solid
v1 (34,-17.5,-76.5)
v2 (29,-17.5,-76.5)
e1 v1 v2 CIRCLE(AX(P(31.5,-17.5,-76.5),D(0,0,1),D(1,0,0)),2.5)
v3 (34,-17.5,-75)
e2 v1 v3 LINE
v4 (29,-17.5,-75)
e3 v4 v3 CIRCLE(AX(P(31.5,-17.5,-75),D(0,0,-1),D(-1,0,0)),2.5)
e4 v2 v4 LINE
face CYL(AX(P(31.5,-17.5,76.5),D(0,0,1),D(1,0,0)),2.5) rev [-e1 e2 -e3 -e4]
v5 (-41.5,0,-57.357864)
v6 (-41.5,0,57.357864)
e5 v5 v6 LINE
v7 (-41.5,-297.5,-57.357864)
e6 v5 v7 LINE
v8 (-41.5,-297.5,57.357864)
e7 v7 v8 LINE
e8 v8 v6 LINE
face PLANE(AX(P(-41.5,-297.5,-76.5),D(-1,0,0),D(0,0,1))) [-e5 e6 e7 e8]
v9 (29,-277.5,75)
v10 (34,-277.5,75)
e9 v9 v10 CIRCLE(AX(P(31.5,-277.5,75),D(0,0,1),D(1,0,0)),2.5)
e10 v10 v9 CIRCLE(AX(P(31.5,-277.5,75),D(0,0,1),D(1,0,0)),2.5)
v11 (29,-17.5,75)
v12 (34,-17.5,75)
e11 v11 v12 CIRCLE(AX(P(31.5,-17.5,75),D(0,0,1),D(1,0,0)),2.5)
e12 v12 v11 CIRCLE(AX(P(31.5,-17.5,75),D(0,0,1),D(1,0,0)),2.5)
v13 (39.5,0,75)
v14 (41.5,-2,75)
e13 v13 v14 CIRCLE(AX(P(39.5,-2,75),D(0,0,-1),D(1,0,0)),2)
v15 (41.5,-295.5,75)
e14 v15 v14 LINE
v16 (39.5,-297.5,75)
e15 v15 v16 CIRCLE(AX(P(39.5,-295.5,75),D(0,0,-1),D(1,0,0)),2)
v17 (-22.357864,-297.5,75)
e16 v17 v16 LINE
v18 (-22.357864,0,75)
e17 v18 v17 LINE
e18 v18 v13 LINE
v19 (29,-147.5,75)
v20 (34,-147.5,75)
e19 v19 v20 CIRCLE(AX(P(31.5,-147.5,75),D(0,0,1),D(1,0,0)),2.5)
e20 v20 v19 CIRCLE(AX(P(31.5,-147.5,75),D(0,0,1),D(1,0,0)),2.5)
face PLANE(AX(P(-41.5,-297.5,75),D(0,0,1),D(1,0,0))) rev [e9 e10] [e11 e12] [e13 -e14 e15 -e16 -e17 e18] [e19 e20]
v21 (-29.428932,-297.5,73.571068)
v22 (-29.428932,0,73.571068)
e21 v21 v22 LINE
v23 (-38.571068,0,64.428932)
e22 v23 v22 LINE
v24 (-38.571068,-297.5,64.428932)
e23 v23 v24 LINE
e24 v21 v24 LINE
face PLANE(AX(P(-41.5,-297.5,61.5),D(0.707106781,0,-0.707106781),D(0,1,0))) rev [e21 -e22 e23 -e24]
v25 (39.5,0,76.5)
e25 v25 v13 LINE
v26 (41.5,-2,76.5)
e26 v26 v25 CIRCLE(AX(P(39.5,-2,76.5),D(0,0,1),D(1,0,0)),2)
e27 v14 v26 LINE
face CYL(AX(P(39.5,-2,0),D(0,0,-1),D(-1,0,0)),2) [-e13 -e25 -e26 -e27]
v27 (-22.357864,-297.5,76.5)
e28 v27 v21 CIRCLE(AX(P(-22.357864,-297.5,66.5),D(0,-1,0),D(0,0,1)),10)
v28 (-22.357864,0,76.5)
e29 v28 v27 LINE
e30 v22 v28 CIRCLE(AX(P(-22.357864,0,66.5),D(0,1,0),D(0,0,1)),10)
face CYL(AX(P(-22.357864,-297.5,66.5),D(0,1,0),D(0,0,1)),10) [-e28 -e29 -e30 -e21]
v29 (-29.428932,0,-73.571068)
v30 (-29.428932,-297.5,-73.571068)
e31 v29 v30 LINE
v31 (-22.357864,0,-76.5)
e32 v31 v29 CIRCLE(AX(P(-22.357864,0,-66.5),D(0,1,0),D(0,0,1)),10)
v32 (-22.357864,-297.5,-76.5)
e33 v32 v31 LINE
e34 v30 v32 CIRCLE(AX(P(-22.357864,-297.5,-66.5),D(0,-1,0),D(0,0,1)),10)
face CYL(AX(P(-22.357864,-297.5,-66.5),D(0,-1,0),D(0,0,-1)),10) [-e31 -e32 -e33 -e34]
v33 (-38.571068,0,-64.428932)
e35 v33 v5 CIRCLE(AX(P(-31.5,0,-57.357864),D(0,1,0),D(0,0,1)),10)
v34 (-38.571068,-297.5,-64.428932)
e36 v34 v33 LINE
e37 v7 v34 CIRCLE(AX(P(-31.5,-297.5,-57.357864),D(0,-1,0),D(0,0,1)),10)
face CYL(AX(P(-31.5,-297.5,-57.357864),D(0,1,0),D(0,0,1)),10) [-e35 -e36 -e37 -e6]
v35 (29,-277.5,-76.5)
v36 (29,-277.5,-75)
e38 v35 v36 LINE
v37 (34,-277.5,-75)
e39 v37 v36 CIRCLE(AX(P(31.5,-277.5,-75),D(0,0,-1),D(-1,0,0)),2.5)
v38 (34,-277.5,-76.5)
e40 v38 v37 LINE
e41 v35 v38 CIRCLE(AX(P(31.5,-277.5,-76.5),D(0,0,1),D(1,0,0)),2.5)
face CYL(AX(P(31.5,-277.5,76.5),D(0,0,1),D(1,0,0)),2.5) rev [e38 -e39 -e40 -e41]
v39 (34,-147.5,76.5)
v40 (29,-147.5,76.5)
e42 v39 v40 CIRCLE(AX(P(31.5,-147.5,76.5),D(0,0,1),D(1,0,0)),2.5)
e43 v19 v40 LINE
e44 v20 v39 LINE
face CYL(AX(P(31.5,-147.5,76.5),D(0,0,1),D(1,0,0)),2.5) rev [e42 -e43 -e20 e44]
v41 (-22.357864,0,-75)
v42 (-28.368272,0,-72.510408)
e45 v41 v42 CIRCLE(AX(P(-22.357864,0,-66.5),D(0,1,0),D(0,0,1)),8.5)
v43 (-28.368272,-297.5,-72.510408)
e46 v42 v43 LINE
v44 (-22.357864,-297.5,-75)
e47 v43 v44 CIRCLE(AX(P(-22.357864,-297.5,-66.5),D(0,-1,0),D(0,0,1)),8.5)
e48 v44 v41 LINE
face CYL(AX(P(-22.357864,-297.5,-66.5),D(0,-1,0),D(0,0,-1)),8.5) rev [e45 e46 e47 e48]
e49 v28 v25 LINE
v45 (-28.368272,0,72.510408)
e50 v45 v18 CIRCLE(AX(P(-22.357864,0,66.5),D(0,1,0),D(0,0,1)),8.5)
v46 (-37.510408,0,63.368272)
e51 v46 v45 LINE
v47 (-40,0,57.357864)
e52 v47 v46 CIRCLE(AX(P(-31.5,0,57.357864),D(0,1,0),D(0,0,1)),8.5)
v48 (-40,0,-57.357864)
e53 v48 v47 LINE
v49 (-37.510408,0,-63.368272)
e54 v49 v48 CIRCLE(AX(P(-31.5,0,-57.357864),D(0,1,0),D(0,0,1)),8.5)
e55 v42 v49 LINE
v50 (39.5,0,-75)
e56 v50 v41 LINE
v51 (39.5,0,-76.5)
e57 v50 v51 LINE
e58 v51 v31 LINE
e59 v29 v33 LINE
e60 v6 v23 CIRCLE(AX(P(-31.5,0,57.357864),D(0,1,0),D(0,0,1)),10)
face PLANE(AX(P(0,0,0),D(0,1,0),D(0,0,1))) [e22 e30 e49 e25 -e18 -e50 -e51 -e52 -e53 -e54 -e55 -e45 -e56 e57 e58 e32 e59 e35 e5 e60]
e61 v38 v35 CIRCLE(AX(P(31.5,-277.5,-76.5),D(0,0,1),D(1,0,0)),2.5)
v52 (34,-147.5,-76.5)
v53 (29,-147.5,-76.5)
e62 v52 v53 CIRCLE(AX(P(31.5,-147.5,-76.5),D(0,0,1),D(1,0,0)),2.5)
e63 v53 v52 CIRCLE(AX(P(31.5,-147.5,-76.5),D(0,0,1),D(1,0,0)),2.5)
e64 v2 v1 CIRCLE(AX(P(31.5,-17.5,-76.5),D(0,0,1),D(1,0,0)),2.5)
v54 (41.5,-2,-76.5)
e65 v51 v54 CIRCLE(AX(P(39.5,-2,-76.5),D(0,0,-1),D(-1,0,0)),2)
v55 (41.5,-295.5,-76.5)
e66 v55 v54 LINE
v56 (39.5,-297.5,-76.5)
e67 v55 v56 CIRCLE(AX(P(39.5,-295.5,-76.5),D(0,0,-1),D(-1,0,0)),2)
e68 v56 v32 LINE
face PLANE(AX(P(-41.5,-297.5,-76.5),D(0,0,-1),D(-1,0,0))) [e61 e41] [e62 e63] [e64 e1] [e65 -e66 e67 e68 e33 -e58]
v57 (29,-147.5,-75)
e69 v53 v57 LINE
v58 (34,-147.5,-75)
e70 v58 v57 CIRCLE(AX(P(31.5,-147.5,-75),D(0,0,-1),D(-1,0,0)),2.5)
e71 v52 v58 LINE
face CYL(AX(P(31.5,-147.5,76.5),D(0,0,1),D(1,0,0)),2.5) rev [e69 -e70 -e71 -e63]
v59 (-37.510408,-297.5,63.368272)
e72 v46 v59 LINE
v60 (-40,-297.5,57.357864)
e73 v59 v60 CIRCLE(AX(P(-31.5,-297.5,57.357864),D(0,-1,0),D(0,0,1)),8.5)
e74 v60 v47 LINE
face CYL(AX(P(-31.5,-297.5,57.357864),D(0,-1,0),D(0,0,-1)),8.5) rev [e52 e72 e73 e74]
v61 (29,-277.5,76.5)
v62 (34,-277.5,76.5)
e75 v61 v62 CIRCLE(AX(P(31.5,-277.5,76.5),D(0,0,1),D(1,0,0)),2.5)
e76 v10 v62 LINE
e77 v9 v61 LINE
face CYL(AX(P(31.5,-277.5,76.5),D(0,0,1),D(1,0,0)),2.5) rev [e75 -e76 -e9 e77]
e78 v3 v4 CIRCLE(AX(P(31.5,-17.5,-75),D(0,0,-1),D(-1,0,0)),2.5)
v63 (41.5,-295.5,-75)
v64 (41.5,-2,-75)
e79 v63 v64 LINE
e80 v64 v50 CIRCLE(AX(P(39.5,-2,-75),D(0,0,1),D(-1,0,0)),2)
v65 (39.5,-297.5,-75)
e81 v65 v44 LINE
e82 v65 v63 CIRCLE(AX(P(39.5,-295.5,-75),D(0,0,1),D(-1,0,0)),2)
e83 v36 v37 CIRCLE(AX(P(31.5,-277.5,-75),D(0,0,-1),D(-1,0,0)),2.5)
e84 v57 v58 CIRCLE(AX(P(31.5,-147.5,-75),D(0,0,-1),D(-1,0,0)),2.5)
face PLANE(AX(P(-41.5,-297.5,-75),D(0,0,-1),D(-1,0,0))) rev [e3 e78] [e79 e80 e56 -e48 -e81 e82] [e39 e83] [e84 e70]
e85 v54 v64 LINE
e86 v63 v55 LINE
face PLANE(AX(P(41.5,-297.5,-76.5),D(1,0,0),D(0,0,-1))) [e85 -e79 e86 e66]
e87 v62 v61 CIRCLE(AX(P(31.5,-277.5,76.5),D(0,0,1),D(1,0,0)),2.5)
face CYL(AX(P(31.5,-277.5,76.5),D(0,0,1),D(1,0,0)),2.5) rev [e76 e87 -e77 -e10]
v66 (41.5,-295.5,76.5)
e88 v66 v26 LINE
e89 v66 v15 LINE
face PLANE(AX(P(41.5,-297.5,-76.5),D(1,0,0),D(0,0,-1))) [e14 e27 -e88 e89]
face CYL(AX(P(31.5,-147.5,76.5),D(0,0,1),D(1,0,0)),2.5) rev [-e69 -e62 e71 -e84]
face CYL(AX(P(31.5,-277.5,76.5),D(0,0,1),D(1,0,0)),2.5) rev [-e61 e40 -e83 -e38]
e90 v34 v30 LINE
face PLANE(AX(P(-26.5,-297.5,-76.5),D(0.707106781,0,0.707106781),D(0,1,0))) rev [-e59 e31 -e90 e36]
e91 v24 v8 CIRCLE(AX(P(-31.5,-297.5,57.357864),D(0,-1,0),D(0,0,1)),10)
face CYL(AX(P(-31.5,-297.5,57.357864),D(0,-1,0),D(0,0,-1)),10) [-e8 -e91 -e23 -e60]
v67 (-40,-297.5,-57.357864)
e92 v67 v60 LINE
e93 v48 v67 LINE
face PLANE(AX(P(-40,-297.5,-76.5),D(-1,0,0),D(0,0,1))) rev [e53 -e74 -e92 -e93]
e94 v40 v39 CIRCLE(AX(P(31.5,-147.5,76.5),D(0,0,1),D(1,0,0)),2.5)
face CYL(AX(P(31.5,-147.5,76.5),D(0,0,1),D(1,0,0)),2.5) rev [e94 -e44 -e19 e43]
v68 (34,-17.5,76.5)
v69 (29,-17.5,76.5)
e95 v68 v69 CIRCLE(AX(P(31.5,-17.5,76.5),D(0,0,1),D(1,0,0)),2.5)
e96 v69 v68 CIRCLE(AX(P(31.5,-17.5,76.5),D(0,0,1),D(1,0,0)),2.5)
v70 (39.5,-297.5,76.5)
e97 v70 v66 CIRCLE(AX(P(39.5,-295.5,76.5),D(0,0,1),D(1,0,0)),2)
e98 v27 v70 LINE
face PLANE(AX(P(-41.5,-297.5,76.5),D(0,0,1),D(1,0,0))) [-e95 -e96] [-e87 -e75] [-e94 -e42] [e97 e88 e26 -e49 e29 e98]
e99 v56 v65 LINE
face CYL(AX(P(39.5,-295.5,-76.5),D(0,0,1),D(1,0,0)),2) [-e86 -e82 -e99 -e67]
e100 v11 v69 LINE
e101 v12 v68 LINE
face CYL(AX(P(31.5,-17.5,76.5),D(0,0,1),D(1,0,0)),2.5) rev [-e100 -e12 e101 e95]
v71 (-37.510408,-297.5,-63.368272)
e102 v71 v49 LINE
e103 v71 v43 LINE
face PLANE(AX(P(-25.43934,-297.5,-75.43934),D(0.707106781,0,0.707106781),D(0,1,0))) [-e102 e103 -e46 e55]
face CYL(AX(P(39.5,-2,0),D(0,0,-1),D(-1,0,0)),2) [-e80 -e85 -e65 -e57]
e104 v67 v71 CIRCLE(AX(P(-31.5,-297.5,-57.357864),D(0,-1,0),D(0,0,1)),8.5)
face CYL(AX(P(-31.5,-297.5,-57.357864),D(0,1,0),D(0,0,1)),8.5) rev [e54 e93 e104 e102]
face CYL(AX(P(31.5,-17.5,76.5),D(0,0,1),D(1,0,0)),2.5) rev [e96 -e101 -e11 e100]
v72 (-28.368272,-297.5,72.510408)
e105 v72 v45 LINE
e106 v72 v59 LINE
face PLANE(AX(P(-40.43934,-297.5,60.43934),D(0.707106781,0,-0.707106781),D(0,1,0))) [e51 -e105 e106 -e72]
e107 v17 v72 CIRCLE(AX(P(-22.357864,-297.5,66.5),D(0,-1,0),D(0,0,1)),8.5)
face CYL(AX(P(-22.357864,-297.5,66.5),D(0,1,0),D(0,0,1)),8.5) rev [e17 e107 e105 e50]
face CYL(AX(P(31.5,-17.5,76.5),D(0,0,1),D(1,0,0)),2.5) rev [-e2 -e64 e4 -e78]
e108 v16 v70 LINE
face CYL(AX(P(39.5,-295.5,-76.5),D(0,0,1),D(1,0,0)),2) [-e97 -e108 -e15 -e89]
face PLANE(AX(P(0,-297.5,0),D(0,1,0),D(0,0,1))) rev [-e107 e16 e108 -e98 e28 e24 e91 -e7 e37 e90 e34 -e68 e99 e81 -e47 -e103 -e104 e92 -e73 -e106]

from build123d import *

# Parameters (mm, degrees)
SKETCH_2_W            = 83
SKETCH_2_H            = 153
EXTRUDE_2_DEPTH       = 297.5
CHAMFER_1_SIZE        = 15
FILLET_1_R            = 10
SHELL_2_T             = -1.5
HOLE_WIZARD_5_0_5_1_D = 5
FILLET_2_R            = 2


with BuildPart() as part:
    # 草图2 → 凸台-拉伸2 (new body)
    with BuildSketch(Plane(origin=(0, 0, 0), x_dir=(1, 0, 0), z_dir=(0, 1, 0))):
        Rectangle(SKETCH_2_W, SKETCH_2_H)
    extrude(amount=-EXTRUDE_2_DEPTH)

    # 倒角1
    chamfer_1_edges = [part.edges().sort_by_distance(p)[0] for p in [
        (-41.5, -148.75, 76.5),
        (-41.5, -148.75, -76.5),
    ]]
    chamfer(chamfer_1_edges, length=CHAMFER_1_SIZE)

    # 圆角1
    fillet_1_edges = [part.edges().sort_by_distance(p)[0] for p in [
        (-26.5, -148.75, -76.5),
        (-41.5, -148.75, 61.5),
        (-41.5, -148.75, -61.5),
        (-26.5, -148.75, 76.5),
    ]]
    fillet(fillet_1_edges, radius=FILLET_1_R)

    # 抽壳2
    shell_2_openings = [part.faces().sort_by_distance(p)[0] for p in [
        (0.682002961, -297.5, 0),
        (0.682002961, 0, 0),
        (41.5, -148.75, 0),
    ]]
    offset(amount=SHELL_2_T, openings=shell_2_openings, kind=Kind.INTERSECTION)

    # Ø5.0 (5) 直径孔1 (through all)
    with Locations(Plane.XY.offset(76.5)):
        with Locations((31.5, -17.5), (31.5, -147.5), (31.5, -277.5)):
            Hole(HOLE_WIZARD_5_0_5_1_D / 2)

    # 圆角2
    fillet_2_edges = [part.edges().sort_by_distance(p)[0] for p in [
        (41.5, -297.5, 75.75),
        (41.5, 0, -75.75),
        (41.5, -297.5, -75.75),
        (41.5, 0, 75.75),
    ]]
    fillet(fillet_2_edges, radius=FILLET_2_R)


solid = part.part
